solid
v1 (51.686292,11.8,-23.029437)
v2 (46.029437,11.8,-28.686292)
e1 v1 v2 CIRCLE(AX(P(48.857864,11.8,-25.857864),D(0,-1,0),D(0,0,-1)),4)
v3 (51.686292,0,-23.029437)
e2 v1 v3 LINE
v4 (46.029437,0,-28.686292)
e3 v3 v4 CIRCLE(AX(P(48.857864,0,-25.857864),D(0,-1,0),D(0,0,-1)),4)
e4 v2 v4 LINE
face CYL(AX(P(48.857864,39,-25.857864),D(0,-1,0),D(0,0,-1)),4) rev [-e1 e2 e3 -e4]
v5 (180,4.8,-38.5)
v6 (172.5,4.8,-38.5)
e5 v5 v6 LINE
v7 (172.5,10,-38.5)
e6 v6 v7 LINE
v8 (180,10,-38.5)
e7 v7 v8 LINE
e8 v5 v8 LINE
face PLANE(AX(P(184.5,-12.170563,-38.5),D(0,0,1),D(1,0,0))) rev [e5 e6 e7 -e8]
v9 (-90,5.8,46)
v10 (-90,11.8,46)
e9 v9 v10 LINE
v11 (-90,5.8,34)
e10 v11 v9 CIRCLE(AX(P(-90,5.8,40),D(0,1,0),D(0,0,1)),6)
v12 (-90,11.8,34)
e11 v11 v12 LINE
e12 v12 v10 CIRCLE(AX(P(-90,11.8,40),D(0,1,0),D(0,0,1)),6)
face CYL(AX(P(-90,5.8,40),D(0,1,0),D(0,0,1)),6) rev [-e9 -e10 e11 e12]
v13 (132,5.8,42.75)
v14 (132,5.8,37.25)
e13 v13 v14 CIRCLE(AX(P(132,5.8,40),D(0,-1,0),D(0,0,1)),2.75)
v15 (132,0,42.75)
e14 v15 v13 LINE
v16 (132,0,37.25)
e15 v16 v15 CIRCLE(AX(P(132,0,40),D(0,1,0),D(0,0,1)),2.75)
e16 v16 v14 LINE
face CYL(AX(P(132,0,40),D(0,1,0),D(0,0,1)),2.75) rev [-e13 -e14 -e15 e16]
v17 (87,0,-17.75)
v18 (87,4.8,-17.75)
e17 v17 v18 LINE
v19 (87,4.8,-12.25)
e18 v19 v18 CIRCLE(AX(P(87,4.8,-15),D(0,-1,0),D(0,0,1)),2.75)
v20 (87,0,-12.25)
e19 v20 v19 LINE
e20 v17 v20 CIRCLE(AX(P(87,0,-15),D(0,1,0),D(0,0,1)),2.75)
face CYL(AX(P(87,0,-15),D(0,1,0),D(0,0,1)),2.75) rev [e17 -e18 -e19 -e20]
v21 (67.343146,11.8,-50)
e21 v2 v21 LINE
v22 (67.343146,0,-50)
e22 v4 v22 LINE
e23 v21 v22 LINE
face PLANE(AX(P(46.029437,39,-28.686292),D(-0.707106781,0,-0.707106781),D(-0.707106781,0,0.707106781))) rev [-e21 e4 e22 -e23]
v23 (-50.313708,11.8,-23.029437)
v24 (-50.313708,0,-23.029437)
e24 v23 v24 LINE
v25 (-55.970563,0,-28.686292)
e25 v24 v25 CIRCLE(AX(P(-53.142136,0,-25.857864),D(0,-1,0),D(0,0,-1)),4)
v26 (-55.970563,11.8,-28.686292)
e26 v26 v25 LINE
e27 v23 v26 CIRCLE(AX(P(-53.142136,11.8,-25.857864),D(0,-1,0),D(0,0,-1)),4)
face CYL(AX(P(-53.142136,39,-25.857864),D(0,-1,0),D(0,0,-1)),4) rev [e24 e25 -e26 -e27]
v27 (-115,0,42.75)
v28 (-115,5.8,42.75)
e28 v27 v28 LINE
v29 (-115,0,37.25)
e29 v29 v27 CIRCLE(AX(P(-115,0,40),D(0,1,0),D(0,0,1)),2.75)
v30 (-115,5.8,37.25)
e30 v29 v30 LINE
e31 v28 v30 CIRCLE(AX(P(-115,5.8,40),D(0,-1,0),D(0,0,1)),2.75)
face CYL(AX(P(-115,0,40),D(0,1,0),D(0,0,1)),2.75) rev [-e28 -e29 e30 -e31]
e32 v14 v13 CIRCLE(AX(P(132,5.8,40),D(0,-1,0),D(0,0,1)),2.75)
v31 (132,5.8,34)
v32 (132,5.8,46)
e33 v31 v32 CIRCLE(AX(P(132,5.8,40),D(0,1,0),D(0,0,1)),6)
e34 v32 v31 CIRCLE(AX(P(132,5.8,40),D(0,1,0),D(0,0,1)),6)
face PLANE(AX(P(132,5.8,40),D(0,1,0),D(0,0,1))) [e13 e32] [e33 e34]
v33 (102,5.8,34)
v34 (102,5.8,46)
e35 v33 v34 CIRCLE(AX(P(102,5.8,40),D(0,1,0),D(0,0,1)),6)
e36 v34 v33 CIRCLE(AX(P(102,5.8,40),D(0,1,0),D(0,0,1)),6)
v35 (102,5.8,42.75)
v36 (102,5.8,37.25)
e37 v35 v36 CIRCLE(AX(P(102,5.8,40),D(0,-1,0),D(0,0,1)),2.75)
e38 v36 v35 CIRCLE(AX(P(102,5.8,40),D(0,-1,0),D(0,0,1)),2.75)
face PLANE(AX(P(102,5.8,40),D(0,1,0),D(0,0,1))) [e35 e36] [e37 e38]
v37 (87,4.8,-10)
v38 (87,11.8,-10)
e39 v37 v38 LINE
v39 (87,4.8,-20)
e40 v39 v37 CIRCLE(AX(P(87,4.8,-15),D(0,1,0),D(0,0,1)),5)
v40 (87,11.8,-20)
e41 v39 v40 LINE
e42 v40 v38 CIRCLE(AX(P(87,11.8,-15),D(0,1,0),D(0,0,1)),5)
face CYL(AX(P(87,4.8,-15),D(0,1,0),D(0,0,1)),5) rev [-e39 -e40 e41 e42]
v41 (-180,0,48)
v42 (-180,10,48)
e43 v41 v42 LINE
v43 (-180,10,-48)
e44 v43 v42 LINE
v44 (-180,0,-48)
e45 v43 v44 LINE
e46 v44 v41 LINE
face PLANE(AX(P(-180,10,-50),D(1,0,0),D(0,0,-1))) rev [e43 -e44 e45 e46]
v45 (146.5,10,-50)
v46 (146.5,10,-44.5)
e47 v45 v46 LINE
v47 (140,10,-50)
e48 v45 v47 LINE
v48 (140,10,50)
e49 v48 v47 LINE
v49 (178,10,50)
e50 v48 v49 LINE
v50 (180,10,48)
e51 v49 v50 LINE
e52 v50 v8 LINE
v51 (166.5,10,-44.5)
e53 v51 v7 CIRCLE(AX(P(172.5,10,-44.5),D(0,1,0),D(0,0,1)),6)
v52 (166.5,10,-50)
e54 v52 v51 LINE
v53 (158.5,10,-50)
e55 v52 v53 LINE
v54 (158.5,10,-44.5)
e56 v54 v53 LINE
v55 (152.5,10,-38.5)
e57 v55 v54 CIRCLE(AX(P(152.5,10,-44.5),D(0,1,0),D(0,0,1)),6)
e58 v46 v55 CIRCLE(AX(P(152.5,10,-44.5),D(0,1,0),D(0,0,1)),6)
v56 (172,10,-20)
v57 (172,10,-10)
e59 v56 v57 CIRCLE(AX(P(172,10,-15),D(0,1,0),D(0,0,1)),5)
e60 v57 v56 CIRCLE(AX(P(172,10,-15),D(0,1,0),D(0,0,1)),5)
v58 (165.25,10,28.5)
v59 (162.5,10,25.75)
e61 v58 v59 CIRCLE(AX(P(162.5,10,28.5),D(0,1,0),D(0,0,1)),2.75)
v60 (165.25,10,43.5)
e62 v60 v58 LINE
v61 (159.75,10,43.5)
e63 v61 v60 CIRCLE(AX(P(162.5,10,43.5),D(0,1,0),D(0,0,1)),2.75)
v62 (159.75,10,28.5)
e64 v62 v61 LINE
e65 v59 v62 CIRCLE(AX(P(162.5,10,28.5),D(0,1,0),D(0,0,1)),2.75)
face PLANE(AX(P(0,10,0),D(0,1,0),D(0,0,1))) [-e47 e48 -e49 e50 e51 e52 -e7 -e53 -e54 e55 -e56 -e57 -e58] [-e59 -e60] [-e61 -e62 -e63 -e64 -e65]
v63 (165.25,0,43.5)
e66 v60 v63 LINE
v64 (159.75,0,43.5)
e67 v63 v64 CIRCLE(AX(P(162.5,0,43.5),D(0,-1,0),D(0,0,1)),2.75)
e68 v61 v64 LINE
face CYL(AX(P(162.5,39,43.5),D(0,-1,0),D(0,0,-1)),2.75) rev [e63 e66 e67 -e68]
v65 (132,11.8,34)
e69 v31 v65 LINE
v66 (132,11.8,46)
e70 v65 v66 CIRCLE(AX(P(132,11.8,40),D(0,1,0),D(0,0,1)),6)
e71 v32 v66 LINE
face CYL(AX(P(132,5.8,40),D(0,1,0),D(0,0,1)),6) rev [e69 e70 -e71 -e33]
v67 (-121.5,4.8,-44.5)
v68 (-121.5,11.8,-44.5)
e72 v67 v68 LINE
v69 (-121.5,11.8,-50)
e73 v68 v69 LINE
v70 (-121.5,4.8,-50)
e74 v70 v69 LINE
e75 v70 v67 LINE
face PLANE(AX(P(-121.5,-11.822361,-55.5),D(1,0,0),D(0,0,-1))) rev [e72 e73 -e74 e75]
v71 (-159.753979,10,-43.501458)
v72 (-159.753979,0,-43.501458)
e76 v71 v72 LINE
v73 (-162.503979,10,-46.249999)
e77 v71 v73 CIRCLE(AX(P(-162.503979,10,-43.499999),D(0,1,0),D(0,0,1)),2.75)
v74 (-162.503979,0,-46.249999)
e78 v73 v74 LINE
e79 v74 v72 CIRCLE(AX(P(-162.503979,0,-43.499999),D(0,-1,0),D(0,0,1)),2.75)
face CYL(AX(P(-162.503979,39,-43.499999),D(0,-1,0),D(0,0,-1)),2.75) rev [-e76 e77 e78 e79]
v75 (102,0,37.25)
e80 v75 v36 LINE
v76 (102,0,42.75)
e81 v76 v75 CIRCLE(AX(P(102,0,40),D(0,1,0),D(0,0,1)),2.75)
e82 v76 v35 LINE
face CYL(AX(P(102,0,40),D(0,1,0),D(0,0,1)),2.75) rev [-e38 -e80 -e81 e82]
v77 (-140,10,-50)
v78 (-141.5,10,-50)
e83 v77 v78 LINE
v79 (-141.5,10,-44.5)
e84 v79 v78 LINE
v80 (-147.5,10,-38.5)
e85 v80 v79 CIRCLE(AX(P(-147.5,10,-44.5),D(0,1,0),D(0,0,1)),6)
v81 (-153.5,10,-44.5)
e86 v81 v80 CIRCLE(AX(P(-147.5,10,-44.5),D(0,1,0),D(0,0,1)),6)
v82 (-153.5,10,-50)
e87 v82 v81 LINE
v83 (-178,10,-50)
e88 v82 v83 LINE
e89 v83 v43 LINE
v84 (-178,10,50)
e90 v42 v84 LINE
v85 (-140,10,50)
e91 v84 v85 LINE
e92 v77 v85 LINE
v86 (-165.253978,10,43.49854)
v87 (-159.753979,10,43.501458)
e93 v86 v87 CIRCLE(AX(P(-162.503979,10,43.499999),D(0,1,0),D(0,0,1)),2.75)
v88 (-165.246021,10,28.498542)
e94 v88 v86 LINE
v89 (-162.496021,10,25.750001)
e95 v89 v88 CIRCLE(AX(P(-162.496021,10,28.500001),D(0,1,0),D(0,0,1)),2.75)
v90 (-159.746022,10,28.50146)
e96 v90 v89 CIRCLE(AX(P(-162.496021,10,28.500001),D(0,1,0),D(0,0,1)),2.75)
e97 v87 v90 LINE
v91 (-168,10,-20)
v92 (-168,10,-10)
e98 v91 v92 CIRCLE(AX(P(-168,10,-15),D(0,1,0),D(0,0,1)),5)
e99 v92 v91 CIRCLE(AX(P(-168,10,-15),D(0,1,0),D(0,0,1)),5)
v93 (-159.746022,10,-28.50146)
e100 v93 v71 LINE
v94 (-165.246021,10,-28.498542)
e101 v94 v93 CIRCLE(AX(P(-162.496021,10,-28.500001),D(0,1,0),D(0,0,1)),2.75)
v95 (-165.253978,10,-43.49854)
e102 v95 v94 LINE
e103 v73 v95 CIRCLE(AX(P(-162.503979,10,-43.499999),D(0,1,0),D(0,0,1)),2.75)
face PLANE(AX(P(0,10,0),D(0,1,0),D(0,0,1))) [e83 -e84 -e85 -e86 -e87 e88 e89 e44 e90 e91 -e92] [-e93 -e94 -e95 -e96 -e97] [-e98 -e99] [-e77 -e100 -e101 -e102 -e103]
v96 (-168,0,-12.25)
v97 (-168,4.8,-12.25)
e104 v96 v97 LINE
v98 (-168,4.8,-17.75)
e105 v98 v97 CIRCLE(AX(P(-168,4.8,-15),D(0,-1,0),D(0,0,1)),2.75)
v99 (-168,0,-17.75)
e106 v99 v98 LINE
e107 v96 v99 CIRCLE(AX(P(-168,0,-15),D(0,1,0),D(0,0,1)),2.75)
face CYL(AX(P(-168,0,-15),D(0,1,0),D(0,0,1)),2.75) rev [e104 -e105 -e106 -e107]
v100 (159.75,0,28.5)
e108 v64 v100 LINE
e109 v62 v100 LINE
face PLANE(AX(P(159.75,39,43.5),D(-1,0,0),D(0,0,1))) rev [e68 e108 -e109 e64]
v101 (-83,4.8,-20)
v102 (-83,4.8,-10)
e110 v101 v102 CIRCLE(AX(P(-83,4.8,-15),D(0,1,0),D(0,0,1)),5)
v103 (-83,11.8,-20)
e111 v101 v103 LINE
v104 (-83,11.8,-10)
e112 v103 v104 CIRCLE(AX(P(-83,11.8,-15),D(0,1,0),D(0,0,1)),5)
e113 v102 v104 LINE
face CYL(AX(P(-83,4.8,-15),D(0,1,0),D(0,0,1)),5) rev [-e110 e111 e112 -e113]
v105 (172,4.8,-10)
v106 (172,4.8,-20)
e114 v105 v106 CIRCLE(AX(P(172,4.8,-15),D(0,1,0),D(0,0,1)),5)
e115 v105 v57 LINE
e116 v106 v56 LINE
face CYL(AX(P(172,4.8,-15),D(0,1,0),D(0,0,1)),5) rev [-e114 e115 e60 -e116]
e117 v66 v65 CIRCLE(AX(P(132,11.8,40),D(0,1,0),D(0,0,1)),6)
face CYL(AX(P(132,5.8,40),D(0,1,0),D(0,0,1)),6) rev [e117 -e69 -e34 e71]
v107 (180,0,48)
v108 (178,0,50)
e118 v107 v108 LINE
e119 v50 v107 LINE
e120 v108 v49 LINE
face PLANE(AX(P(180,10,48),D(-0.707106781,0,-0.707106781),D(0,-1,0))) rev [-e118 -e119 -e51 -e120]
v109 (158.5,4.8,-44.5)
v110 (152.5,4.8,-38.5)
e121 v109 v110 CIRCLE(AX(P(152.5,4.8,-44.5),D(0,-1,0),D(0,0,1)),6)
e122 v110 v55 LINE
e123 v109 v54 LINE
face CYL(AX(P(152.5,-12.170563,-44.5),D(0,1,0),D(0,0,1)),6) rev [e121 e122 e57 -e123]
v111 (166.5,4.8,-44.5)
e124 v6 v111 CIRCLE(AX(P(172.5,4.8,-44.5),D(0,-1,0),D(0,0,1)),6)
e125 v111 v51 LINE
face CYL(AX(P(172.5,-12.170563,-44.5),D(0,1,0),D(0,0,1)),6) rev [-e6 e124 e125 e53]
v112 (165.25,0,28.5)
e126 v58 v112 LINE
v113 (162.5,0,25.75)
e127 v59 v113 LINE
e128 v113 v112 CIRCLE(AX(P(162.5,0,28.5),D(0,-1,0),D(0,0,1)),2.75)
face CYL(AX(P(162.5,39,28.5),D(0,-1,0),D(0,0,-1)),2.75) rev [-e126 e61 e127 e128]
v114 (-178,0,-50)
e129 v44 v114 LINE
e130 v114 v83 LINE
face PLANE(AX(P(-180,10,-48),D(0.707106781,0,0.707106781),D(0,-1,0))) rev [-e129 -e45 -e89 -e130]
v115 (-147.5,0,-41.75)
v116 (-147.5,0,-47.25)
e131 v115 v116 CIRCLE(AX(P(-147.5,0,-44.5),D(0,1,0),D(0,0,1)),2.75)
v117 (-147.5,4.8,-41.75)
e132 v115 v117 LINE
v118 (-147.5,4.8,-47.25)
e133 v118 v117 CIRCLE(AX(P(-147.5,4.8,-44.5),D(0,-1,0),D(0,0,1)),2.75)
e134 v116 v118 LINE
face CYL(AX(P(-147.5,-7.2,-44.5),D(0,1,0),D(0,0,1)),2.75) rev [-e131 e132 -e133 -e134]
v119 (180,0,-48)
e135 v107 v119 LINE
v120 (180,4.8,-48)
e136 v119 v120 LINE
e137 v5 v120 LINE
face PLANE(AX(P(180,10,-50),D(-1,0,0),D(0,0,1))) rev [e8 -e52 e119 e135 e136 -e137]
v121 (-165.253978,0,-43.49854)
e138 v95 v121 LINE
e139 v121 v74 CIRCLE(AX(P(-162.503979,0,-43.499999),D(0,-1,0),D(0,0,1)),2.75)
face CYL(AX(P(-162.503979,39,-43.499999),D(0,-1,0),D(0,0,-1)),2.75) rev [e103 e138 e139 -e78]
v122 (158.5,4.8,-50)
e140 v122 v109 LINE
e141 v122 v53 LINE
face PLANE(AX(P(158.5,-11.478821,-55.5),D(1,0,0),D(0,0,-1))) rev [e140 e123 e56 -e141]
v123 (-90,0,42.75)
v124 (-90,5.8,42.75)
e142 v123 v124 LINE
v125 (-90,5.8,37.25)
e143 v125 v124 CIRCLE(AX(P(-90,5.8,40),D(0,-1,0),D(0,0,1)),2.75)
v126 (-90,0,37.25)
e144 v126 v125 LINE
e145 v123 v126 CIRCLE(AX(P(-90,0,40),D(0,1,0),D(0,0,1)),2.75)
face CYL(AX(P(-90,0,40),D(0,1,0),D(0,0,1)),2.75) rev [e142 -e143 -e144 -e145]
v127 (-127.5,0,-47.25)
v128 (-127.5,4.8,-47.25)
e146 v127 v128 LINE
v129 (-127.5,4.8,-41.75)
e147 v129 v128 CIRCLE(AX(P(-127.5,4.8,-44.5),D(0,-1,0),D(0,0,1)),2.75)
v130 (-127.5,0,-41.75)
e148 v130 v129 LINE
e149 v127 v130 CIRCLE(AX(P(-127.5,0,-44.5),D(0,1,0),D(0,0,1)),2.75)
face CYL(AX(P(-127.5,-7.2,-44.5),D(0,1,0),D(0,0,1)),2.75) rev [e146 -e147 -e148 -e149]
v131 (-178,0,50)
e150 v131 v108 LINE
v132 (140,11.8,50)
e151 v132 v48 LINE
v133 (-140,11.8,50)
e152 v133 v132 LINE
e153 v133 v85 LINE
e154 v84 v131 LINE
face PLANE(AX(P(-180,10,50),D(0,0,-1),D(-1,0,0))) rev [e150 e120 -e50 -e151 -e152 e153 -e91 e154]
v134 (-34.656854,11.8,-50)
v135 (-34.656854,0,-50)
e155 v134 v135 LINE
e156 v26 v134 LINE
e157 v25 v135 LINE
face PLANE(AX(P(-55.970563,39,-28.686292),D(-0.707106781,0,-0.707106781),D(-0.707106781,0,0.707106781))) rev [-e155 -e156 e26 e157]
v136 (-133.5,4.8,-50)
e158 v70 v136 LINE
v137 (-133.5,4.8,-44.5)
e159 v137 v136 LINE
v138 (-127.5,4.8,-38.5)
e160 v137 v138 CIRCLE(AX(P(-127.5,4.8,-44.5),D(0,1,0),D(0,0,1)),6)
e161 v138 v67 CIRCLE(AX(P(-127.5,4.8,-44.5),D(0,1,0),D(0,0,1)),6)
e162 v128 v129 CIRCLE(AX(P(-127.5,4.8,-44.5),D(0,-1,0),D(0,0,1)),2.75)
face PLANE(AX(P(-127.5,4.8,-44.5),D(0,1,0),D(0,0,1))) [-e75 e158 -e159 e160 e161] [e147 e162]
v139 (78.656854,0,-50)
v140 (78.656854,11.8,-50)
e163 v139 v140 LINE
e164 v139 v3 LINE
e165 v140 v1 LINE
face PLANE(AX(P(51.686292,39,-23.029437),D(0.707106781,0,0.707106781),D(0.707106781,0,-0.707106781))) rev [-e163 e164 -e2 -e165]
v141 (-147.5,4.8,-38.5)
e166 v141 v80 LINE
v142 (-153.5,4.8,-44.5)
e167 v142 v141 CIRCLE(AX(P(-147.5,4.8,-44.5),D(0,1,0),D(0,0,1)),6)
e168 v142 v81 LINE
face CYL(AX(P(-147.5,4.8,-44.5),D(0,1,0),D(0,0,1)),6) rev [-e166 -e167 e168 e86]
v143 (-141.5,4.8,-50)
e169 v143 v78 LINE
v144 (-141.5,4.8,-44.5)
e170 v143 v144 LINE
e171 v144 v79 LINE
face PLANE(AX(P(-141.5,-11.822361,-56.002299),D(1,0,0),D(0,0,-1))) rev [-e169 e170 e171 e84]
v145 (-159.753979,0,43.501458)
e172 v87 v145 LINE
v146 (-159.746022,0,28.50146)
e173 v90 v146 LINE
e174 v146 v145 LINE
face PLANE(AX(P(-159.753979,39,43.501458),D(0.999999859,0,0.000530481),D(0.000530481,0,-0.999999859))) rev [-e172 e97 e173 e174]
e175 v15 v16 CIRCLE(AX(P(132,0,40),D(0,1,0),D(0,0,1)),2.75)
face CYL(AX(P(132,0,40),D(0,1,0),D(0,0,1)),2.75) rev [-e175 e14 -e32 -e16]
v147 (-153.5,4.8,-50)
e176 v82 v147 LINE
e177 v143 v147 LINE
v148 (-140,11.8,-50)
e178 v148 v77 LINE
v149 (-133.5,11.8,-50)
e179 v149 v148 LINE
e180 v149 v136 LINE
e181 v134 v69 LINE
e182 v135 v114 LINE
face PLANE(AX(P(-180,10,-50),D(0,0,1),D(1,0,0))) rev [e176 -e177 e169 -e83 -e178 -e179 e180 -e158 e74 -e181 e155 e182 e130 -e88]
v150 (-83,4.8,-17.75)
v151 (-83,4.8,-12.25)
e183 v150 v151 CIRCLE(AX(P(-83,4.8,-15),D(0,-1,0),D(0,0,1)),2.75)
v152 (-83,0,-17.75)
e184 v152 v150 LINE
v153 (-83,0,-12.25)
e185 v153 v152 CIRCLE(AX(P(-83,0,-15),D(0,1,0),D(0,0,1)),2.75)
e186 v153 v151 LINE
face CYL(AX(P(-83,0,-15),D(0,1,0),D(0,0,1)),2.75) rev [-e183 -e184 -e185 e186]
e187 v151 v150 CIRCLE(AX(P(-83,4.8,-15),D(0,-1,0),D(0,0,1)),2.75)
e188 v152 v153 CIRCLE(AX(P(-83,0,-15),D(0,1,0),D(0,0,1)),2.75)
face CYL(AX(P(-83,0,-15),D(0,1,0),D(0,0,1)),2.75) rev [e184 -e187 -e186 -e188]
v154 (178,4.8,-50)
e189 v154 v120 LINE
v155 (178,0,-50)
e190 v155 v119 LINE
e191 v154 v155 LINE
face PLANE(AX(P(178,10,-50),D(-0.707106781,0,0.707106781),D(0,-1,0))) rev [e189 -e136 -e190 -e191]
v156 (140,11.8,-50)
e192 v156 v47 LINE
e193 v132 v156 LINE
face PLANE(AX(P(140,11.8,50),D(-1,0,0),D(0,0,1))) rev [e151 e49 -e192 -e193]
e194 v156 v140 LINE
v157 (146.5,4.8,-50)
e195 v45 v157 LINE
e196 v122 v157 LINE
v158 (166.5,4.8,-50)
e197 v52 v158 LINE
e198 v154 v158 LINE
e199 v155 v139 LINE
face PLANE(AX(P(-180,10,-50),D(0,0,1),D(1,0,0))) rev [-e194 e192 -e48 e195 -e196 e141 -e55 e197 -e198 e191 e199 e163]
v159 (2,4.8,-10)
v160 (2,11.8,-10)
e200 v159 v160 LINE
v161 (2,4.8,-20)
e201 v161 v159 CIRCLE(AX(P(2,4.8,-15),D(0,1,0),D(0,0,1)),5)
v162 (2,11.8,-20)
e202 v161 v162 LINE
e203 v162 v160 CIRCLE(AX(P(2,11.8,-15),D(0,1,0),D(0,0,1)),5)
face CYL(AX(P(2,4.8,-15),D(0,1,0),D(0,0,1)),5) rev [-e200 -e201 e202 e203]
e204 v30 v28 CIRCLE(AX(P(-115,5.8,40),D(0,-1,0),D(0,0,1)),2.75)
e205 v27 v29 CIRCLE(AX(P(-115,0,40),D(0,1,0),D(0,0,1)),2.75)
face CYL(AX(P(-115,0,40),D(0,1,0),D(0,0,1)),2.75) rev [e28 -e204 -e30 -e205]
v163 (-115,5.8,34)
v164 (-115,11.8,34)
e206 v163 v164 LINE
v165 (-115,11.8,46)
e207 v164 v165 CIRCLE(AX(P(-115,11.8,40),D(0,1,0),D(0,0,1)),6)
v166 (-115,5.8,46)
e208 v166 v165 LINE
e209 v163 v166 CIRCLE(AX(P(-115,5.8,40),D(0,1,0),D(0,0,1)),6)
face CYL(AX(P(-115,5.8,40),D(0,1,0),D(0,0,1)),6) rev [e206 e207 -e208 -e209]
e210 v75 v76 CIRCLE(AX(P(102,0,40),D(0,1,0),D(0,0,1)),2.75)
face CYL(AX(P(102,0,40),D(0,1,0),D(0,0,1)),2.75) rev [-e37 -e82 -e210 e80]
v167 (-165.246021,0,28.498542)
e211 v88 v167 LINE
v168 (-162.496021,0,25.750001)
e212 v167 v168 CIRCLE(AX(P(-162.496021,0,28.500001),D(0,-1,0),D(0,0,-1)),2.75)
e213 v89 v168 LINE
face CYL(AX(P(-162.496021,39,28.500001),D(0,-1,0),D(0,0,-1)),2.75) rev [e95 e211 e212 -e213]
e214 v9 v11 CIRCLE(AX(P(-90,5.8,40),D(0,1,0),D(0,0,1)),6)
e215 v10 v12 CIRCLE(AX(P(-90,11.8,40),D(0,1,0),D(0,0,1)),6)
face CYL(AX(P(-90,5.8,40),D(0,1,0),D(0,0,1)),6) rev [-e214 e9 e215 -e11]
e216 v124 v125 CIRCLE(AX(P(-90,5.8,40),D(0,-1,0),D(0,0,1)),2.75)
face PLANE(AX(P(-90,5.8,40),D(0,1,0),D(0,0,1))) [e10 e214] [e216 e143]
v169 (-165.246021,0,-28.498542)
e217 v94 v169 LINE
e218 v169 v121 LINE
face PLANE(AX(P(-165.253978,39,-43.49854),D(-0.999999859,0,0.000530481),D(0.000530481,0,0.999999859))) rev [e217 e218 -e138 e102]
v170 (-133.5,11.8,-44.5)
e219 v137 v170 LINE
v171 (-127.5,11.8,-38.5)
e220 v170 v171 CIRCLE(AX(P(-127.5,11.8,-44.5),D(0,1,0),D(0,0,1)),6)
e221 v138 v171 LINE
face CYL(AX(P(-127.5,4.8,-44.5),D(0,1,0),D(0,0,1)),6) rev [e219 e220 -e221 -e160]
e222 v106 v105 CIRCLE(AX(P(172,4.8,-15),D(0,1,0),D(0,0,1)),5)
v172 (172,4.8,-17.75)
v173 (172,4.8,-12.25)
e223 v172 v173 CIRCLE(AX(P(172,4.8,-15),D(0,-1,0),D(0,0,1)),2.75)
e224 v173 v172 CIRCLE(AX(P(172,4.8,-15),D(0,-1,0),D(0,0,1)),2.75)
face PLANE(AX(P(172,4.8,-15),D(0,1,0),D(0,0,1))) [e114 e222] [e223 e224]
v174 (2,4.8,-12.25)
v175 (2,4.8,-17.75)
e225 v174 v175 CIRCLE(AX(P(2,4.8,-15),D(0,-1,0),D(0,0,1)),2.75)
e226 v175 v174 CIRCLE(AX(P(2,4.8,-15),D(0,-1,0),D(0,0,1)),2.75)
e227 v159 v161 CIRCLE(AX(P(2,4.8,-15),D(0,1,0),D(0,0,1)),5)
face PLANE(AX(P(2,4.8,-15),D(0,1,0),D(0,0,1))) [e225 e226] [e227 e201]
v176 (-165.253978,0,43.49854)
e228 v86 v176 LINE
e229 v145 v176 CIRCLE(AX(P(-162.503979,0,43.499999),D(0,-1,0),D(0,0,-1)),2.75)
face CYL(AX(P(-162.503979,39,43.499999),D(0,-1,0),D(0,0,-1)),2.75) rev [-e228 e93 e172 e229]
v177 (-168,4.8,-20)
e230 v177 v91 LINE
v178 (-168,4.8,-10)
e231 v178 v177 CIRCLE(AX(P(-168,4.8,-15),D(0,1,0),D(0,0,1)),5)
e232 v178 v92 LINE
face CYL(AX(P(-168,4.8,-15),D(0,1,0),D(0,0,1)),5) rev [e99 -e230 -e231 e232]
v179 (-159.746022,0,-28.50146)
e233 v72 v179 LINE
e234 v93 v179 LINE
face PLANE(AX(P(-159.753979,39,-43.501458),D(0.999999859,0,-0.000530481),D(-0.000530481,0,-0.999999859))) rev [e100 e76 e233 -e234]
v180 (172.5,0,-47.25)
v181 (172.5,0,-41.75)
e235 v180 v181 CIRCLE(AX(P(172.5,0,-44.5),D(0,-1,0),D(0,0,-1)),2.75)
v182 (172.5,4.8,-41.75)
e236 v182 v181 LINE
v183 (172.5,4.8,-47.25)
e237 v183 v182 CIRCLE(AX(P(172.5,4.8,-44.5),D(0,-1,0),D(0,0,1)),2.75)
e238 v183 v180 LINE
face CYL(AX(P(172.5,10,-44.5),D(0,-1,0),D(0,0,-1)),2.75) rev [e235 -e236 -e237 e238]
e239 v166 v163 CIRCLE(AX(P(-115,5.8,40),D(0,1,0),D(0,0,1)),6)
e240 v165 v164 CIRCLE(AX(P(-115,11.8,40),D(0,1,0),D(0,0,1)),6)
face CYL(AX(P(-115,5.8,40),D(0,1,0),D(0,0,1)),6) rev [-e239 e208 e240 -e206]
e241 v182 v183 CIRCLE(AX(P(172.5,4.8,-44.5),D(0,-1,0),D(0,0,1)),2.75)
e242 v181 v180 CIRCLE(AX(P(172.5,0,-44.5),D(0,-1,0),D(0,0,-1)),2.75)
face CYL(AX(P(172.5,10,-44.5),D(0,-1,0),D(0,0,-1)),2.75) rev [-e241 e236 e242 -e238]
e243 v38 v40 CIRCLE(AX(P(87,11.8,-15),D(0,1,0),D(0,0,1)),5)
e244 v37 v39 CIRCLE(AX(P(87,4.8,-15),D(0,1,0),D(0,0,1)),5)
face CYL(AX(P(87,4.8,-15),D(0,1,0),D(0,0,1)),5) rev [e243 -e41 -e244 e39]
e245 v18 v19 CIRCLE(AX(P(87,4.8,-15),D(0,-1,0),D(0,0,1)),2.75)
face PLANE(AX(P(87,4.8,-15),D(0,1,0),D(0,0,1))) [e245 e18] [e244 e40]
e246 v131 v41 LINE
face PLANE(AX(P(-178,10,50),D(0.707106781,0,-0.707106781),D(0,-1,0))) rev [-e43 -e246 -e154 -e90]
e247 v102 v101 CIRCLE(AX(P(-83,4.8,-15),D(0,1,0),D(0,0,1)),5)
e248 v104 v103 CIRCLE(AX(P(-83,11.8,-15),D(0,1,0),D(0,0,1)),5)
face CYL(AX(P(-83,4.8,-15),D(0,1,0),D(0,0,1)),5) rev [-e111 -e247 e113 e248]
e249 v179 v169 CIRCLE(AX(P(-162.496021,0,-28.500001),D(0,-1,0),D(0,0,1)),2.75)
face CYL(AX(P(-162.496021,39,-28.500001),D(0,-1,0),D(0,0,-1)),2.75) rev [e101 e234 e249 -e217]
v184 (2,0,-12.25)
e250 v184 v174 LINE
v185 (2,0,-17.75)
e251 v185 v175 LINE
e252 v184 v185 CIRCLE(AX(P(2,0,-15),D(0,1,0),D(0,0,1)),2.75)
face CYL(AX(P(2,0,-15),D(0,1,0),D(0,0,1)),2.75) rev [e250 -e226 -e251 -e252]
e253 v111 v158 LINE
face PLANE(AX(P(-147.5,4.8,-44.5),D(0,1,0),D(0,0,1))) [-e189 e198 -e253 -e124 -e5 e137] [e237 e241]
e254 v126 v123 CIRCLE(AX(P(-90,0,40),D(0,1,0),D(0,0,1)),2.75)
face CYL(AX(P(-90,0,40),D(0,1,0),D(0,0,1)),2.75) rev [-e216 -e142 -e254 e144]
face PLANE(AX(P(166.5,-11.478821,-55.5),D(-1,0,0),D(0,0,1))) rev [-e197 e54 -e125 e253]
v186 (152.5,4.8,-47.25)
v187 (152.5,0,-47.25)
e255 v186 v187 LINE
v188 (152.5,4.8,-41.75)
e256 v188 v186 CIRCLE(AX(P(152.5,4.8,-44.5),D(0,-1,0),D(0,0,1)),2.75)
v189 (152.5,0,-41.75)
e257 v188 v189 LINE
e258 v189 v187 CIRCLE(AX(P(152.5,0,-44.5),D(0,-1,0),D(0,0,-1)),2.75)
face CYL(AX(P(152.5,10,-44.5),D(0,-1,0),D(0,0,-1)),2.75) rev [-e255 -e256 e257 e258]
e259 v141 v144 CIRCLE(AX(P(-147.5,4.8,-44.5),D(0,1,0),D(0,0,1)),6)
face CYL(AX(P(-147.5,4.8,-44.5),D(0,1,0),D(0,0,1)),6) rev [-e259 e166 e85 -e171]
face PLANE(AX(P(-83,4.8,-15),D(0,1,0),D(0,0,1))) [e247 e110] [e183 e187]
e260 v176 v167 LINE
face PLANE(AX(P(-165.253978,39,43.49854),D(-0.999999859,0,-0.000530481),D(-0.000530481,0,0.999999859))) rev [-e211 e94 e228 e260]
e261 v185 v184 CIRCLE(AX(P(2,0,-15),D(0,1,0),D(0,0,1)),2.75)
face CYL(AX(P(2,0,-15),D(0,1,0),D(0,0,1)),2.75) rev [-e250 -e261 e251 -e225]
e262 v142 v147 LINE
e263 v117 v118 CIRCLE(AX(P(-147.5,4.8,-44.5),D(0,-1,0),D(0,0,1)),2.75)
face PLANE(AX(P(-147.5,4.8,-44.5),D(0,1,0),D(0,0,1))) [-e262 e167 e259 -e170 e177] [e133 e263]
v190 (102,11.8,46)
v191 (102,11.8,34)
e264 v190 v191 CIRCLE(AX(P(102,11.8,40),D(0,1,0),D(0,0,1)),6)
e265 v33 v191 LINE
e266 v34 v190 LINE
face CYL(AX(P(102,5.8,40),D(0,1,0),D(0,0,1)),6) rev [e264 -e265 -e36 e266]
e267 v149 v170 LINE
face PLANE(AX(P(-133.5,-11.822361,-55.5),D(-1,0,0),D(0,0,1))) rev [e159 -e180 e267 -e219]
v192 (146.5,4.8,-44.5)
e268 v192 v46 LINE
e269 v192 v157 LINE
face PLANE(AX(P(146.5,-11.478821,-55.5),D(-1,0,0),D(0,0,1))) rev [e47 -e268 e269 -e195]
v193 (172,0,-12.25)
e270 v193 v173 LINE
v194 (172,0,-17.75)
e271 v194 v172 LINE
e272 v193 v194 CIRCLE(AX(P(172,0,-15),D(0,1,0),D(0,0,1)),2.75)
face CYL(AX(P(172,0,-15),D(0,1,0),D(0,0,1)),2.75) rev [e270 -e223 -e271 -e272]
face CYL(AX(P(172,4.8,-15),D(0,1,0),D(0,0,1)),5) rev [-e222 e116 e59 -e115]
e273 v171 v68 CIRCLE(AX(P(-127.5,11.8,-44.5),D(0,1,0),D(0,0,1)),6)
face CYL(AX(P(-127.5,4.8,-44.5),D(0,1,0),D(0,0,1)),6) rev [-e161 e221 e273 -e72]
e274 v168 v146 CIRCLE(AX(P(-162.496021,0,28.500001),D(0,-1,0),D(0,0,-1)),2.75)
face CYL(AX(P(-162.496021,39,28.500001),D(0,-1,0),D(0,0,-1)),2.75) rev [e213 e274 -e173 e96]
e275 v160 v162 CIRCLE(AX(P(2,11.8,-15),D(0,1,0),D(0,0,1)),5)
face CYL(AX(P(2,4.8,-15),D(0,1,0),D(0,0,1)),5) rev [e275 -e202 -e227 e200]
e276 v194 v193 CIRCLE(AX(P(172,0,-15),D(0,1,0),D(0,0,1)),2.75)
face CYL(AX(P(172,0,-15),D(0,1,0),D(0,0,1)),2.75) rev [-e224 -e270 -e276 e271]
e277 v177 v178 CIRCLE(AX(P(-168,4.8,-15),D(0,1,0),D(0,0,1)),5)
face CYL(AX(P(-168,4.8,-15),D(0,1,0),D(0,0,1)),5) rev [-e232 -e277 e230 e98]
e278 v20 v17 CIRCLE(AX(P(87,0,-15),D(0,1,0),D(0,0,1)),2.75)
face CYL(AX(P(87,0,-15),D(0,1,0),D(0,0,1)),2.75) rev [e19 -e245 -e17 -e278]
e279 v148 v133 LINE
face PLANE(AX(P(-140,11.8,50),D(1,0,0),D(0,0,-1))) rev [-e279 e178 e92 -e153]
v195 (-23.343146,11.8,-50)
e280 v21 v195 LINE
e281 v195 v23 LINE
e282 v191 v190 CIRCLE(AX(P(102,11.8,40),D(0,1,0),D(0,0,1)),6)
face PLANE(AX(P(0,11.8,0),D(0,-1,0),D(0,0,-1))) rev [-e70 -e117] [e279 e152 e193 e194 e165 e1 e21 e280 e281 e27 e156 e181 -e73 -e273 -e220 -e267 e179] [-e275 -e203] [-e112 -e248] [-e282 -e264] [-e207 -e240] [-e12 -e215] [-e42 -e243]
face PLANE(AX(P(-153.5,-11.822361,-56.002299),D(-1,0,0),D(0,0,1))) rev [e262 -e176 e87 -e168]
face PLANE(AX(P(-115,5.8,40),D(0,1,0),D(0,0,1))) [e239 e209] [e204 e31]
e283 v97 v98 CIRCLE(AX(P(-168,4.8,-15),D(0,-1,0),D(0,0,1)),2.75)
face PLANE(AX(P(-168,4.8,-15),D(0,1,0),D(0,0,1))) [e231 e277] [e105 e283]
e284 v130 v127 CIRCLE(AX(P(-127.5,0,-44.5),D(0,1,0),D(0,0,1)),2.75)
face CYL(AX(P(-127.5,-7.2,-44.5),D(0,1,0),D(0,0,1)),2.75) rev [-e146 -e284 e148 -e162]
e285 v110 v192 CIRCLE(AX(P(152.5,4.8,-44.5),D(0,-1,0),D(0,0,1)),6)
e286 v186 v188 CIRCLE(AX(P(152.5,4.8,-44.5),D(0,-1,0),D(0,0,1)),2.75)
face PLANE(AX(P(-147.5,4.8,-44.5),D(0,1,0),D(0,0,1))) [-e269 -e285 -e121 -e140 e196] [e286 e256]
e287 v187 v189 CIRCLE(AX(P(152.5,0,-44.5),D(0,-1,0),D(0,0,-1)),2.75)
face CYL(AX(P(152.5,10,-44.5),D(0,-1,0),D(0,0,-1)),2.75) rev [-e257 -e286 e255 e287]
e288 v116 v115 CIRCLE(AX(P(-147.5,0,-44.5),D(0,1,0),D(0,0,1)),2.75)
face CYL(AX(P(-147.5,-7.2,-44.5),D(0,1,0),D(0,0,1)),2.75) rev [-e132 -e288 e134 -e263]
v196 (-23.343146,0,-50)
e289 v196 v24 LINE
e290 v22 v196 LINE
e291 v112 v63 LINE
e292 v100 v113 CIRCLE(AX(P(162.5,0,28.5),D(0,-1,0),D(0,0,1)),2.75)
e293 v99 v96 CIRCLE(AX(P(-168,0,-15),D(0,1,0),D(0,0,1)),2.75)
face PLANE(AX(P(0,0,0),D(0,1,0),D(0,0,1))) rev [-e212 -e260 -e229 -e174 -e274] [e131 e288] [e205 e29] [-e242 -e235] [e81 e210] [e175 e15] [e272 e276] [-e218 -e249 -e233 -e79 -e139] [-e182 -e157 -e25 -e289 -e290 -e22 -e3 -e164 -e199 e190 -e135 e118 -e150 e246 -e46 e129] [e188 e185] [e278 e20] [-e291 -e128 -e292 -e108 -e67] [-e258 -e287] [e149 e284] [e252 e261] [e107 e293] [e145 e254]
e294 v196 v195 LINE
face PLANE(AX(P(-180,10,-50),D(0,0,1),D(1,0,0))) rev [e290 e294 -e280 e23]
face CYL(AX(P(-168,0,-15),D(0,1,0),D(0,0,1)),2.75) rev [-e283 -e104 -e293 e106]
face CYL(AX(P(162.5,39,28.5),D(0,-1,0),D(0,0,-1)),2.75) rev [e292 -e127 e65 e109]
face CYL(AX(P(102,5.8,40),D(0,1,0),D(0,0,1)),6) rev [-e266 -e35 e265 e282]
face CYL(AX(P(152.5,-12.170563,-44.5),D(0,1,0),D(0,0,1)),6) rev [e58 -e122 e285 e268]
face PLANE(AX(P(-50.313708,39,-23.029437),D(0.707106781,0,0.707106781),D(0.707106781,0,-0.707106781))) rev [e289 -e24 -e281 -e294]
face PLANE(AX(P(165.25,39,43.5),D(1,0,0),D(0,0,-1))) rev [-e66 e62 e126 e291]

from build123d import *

# Parameters (mm, degrees)
SKETCH1_W           = 360
SKETCH1_H           = 100
BOSS_EXTRUDE1_DEPTH = 10
SKETCH2_W           = 280
SKETCH2_H           = 100
BOSS_EXTRUDE2_DEPTH = 1.8
SKETCH3_R           = 4
CUT_EXTRUDE1_DEPTH  = 188.187713272
CUT_EXTRUDE2_DEPTH  = 39
CUT_EXTRUDE3_DEPTH  = 39
CHAMFER1_SIZE       = 2
SKETCH6_R           = 2.75
CUT_EXTRUDE4_DEPTH  = 188.187713272
SKETCH7_R           = 6
CUT_EXTRUDE5_DEPTH  = 6
SKETCH8_R           = 2.75
CUT_EXTRUDE6_DEPTH  = 19
SKETCH9_R           = 6
CUT_EXTRUDE7_DEPTH  = 7
SKETCH11_W          = 12
SKETCH11_H          = 11.502298529
SKETCH11_H_2        = 11
CUT_EXTRUDE8_DEPTH  = 7
SKETCH12_R          = 2.75
CUT_EXTRUDE9_DEPTH  = 188.187713272
LPATTERN1_COUNT     = 5
LPATTERN1_PITCH     = 85
SKETCH13_R          = 5
CUT_EXTRUDE10_DEPTH = 7
SKETCH14_R          = 2.75
CUT_EXTRUDE11_DEPTH = 10
SKETCH15_R          = 6
CUT_EXTRUDE12_DEPTH = 5.2
SKETCH16_W          = 12
SKETCH16_H          = 11
CUT_EXTRUDE13_DEPTH = 5.2
SKETCH17_W          = 12
SKETCH17_H          = 12
CUT_EXTRUDE14_DEPTH = 5.2


with BuildPart() as part:
    # Sketch1 → Boss-Extrude1 (new body)
    with BuildSketch(Plane(origin=(0, 0, 0), x_dir=(1, 0, 0), z_dir=(0, 1, 0))):
        Rectangle(SKETCH1_W, SKETCH1_H)
    extrude(amount=BOSS_EXTRUDE1_DEPTH)

    # Sketch2 → Boss-Extrude2 (add)
    with BuildSketch(Plane(origin=(0, 10, 0), x_dir=(1, 0, 0), z_dir=(0, 1, 0))):
        Rectangle(SKETCH2_W, SKETCH2_H)
    extrude(amount=BOSS_EXTRUDE2_DEPTH)

    # Sketch3 → Cut-Extrude1 (cut, through all)
    with BuildSketch(Plane.XZ):
        with Locations(Location((-39, -40, 0), (0, 0, 270))):
            Circle(SKETCH3_R)
        with Locations(Location((63, -40, 0), (0, 0, 270))):
            Circle(SKETCH3_R)
    extrude(amount=-CUT_EXTRUDE1_DEPTH, mode=Mode.SUBTRACT)

    # Sketch4 → Cut-Extrude2 (cut)
    with BuildSketch(Plane.XZ):
        with BuildLine():
            Line((51.686291501, -23.029437252), (79.970562748, -51.313708499))
            ThreePointArc((79.970562748, -51.313708499), (79.970562748, -56.970562748), (74.313708499, -56.970562748))
            Line((74.313708499, -56.970562748), (46.029437252, -28.686291501))
            ThreePointArc((46.029437252, -28.686291501), (46.029437252, -23.029437252), (51.686291501, -23.029437252))
        make_face()
        with BuildLine():
            Line((-50.313708499, -23.029437252), (-22.029437252, -51.313708499))
            ThreePointArc((-22.029437252, -51.313708499), (-22.029437252, -56.970562748), (-27.686291501, -56.970562748))
            Line((-27.686291501, -56.970562748), (-55.970562748, -28.686291501))
            ThreePointArc((-55.970562748, -28.686291501), (-55.970562748, -23.029437252), (-50.313708499, -23.029437252))
        make_face()
    extrude(amount=-CUT_EXTRUDE2_DEPTH, mode=Mode.SUBTRACT)

    # Sketch5 → Cut-Extrude3 (cut)
    with BuildSketch(Plane.XZ):
        with BuildLine():
            Line((-159.753978998, 43.501457769), (-159.746021776, 28.501459879))
            ThreePointArc((-159.746021776, 28.501459879), (-162.494562565, 25.750001442), (-165.246021002, 28.498542231))
            Line((-165.246021002, 28.498542231), (-165.253978224, 43.498540121))
            ThreePointArc((-165.253978224, 43.498540121), (-162.505437435, 46.249998558), (-159.753978998, 43.501457769))
        make_face()
        with BuildLine():
            Line((159.75, 43.5), (159.75, 28.5))
            ThreePointArc((159.75, 28.5), (162.5, 25.75), (165.25, 28.5))
            Line((165.25, 28.5), (165.25, 43.5))
            ThreePointArc((165.25, 43.5), (162.5, 46.25), (159.75, 43.5))
        make_face()
        with BuildLine():
            Line((-159.753978998, -43.501457769), (-159.746021776, -28.501459879))
            ThreePointArc((-159.746021776, -28.501459879), (-162.494562565, -25.750001442), (-165.246021002, -28.498542231))
            Line((-165.246021002, -28.498542231), (-165.253978224, -43.498540121))
            ThreePointArc((-165.253978224, -43.498540121), (-162.505437435, -46.249998558), (-159.753978998, -43.501457769))
        make_face()
    extrude(amount=-CUT_EXTRUDE3_DEPTH, mode=Mode.SUBTRACT)

    # Chamfer1
    chamfer1_edges = [part.edges().sort_by_distance(p)[0] for p in [
        (180, 5, 50),
        (-180, 5, 50),
        (-180, 5, -50),
        (180, 5, -50),
    ]]
    chamfer(chamfer1_edges, length=CHAMFER1_SIZE)

    # Sketch6 → Cut-Extrude4 (cut, through all)
    with BuildSketch(Plane(origin=(0, 11.8, 0), x_dir=(1, 0, 0), z_dir=(0, 1, 0))):
        with Locations(Location((132, -40, 0), (0, 0, 270))):
            Circle(SKETCH6_R)
        with Locations(Location((102, -40, 0), (0, 0, 270))):
            Circle(SKETCH6_R)
        with Locations(Location((-90, -40, 0), (0, 0, 270))):
            Circle(SKETCH6_R)
        with Locations(Location((-115, -40, 0), (0, 0, 270))):
            Circle(SKETCH6_R)
    extrude(amount=-CUT_EXTRUDE4_DEPTH, mode=Mode.SUBTRACT)

    # Sketch7 → Cut-Extrude5 (cut)
    with BuildSketch(Plane(origin=(0, 11.8, 0), x_dir=(1, 0, 0), z_dir=(0, 1, 0))):
        with Locations(Location((-115, -40, 0), (0, 0, 270))):
            Circle(SKETCH7_R)
        with Locations(Location((-90, -40, 0), (0, 0, 270))):
            Circle(SKETCH7_R)
        with Locations(Location((102, -40, 0), (0, 0, 270))):
            Circle(SKETCH7_R)
        with Locations(Location((132, -40, 0), (0, 0, 270))):
            Circle(SKETCH7_R)
    extrude(amount=-CUT_EXTRUDE5_DEPTH, mode=Mode.SUBTRACT)

    # Sketch8 → Cut-Extrude6 (cut)
    with BuildSketch(Plane(origin=(0, 11.8, 0), x_dir=(1, 0, 0), z_dir=(0, 1, 0))):
        with Locations(Location((-147.5, 44.5, 0), (0, 0, 270))):
            Circle(SKETCH8_R)
        with Locations(Location((-127.5, 44.5, 0), (0, 0, 270))):
            Circle(SKETCH8_R)
    extrude(amount=-CUT_EXTRUDE6_DEPTH, mode=Mode.SUBTRACT)

    # Sketch9 → Cut-Extrude7 (cut)
    with BuildSketch(Plane(origin=(0, 11.8, 0), x_dir=(1, 0, 0), z_dir=(0, 1, 0))):
        with Locations((-147.5, 44.5)):
            Circle(SKETCH9_R)
        with Locations((-127.5, 44.5)):
            Circle(SKETCH9_R)
    extrude(amount=-CUT_EXTRUDE7_DEPTH, mode=Mode.SUBTRACT)

    # Sketch11 → Cut-Extrude8 (cut)
    with BuildSketch(Plane(origin=(0, 11.8, 0), x_dir=(1, 0, 0), z_dir=(0, 1, 0))):
        with Locations((-147.5, 50.251149265)):
            Rectangle(SKETCH11_W, SKETCH11_H)
        with Locations((-127.5, 50)):
            Rectangle(SKETCH11_W, SKETCH11_H_2)
    extrude(amount=-CUT_EXTRUDE8_DEPTH, mode=Mode.SUBTRACT)

    # Sketch12 → Cut-Extrude9 (cut, through all)
    with BuildSketch(Plane(origin=(0, 11.8, 0), x_dir=(1, 0, 0), z_dir=(0, 1, 0))):
        with Locations(Location((-168, 15, 0), (0, 0, 270))):
            Circle(SKETCH12_R)
    cut_extrude9 = extrude(amount=-CUT_EXTRUDE9_DEPTH, mode=Mode.SUBTRACT)

    # LPattern1: Cut-Extrude9 ×5
    with Locations(*[(i * LPATTERN1_PITCH, 0, 0) for i in range(1, LPATTERN1_COUNT)]):
        add(cut_extrude9, mode=Mode.SUBTRACT)

    # Sketch13 → Cut-Extrude10 (cut)
    with BuildSketch(Plane(origin=(0, 11.8, 0), x_dir=(1, 0, 0), z_dir=(0, 1, 0))):
        with Locations(Location((172, 15, 0), (0, 0, 270))):
            Circle(SKETCH13_R)
        with Locations(Location((87, 15, 0), (0, 0, 270))):
            Circle(SKETCH13_R)
        with Locations(Location((2, 15, 0), (0, 0, 270))):
            Circle(SKETCH13_R)
        with Locations(Location((-83, 15, 0), (0, 0, 270))):
            Circle(SKETCH13_R)
        with Locations(Location((-168, 15, 0), (0, 0, 270))):
            Circle(SKETCH13_R)
    extrude(amount=-CUT_EXTRUDE10_DEPTH, mode=Mode.SUBTRACT)

    # Sketch14 → Cut-Extrude11 (cut)
    with BuildSketch(Plane.XZ):
        with Locations(Location((152.5, -44.5, 0), (0, 0, 270))):
            Circle(SKETCH14_R)
        with Locations(Location((172.5, -44.5, 0), (0, 0, 270))):
            Circle(SKETCH14_R)
    extrude(amount=-CUT_EXTRUDE11_DEPTH, mode=Mode.SUBTRACT)

    # Sketch15 → Cut-Extrude12 (cut)
    with BuildSketch(Plane(origin=(0, 10, 0), x_dir=(1, 0, 0), z_dir=(0, 1, 0))):
        with Locations((152.5, 44.5)):
            Circle(SKETCH15_R)
        with Locations((172.5, 44.5)):
            Circle(SKETCH15_R)
    extrude(amount=-CUT_EXTRUDE12_DEPTH, mode=Mode.SUBTRACT)

    # Sketch16 → Cut-Extrude13 (cut)
    with BuildSketch(Plane(origin=(0, 10, 0), x_dir=(1, 0, 0), z_dir=(0, 1, 0))):
        with Locations((152.5, 50)):
            Rectangle(SKETCH16_W, SKETCH16_H)
        with Locations((172.5, 50)):
            Rectangle(SKETCH16_W, SKETCH16_H)
    extrude(amount=-CUT_EXTRUDE13_DEPTH, mode=Mode.SUBTRACT)

    # Sketch17 → Cut-Extrude14 (cut)
    with BuildSketch(Plane(origin=(0, 10, 0), x_dir=(1, 0, 0), z_dir=(0, 1, 0))):
        with Locations((178.5, 44.5)):
            Rectangle(SKETCH17_W, SKETCH17_H)
    extrude(amount=-CUT_EXTRUDE14_DEPTH, mode=Mode.SUBTRACT)


solid = part.part
